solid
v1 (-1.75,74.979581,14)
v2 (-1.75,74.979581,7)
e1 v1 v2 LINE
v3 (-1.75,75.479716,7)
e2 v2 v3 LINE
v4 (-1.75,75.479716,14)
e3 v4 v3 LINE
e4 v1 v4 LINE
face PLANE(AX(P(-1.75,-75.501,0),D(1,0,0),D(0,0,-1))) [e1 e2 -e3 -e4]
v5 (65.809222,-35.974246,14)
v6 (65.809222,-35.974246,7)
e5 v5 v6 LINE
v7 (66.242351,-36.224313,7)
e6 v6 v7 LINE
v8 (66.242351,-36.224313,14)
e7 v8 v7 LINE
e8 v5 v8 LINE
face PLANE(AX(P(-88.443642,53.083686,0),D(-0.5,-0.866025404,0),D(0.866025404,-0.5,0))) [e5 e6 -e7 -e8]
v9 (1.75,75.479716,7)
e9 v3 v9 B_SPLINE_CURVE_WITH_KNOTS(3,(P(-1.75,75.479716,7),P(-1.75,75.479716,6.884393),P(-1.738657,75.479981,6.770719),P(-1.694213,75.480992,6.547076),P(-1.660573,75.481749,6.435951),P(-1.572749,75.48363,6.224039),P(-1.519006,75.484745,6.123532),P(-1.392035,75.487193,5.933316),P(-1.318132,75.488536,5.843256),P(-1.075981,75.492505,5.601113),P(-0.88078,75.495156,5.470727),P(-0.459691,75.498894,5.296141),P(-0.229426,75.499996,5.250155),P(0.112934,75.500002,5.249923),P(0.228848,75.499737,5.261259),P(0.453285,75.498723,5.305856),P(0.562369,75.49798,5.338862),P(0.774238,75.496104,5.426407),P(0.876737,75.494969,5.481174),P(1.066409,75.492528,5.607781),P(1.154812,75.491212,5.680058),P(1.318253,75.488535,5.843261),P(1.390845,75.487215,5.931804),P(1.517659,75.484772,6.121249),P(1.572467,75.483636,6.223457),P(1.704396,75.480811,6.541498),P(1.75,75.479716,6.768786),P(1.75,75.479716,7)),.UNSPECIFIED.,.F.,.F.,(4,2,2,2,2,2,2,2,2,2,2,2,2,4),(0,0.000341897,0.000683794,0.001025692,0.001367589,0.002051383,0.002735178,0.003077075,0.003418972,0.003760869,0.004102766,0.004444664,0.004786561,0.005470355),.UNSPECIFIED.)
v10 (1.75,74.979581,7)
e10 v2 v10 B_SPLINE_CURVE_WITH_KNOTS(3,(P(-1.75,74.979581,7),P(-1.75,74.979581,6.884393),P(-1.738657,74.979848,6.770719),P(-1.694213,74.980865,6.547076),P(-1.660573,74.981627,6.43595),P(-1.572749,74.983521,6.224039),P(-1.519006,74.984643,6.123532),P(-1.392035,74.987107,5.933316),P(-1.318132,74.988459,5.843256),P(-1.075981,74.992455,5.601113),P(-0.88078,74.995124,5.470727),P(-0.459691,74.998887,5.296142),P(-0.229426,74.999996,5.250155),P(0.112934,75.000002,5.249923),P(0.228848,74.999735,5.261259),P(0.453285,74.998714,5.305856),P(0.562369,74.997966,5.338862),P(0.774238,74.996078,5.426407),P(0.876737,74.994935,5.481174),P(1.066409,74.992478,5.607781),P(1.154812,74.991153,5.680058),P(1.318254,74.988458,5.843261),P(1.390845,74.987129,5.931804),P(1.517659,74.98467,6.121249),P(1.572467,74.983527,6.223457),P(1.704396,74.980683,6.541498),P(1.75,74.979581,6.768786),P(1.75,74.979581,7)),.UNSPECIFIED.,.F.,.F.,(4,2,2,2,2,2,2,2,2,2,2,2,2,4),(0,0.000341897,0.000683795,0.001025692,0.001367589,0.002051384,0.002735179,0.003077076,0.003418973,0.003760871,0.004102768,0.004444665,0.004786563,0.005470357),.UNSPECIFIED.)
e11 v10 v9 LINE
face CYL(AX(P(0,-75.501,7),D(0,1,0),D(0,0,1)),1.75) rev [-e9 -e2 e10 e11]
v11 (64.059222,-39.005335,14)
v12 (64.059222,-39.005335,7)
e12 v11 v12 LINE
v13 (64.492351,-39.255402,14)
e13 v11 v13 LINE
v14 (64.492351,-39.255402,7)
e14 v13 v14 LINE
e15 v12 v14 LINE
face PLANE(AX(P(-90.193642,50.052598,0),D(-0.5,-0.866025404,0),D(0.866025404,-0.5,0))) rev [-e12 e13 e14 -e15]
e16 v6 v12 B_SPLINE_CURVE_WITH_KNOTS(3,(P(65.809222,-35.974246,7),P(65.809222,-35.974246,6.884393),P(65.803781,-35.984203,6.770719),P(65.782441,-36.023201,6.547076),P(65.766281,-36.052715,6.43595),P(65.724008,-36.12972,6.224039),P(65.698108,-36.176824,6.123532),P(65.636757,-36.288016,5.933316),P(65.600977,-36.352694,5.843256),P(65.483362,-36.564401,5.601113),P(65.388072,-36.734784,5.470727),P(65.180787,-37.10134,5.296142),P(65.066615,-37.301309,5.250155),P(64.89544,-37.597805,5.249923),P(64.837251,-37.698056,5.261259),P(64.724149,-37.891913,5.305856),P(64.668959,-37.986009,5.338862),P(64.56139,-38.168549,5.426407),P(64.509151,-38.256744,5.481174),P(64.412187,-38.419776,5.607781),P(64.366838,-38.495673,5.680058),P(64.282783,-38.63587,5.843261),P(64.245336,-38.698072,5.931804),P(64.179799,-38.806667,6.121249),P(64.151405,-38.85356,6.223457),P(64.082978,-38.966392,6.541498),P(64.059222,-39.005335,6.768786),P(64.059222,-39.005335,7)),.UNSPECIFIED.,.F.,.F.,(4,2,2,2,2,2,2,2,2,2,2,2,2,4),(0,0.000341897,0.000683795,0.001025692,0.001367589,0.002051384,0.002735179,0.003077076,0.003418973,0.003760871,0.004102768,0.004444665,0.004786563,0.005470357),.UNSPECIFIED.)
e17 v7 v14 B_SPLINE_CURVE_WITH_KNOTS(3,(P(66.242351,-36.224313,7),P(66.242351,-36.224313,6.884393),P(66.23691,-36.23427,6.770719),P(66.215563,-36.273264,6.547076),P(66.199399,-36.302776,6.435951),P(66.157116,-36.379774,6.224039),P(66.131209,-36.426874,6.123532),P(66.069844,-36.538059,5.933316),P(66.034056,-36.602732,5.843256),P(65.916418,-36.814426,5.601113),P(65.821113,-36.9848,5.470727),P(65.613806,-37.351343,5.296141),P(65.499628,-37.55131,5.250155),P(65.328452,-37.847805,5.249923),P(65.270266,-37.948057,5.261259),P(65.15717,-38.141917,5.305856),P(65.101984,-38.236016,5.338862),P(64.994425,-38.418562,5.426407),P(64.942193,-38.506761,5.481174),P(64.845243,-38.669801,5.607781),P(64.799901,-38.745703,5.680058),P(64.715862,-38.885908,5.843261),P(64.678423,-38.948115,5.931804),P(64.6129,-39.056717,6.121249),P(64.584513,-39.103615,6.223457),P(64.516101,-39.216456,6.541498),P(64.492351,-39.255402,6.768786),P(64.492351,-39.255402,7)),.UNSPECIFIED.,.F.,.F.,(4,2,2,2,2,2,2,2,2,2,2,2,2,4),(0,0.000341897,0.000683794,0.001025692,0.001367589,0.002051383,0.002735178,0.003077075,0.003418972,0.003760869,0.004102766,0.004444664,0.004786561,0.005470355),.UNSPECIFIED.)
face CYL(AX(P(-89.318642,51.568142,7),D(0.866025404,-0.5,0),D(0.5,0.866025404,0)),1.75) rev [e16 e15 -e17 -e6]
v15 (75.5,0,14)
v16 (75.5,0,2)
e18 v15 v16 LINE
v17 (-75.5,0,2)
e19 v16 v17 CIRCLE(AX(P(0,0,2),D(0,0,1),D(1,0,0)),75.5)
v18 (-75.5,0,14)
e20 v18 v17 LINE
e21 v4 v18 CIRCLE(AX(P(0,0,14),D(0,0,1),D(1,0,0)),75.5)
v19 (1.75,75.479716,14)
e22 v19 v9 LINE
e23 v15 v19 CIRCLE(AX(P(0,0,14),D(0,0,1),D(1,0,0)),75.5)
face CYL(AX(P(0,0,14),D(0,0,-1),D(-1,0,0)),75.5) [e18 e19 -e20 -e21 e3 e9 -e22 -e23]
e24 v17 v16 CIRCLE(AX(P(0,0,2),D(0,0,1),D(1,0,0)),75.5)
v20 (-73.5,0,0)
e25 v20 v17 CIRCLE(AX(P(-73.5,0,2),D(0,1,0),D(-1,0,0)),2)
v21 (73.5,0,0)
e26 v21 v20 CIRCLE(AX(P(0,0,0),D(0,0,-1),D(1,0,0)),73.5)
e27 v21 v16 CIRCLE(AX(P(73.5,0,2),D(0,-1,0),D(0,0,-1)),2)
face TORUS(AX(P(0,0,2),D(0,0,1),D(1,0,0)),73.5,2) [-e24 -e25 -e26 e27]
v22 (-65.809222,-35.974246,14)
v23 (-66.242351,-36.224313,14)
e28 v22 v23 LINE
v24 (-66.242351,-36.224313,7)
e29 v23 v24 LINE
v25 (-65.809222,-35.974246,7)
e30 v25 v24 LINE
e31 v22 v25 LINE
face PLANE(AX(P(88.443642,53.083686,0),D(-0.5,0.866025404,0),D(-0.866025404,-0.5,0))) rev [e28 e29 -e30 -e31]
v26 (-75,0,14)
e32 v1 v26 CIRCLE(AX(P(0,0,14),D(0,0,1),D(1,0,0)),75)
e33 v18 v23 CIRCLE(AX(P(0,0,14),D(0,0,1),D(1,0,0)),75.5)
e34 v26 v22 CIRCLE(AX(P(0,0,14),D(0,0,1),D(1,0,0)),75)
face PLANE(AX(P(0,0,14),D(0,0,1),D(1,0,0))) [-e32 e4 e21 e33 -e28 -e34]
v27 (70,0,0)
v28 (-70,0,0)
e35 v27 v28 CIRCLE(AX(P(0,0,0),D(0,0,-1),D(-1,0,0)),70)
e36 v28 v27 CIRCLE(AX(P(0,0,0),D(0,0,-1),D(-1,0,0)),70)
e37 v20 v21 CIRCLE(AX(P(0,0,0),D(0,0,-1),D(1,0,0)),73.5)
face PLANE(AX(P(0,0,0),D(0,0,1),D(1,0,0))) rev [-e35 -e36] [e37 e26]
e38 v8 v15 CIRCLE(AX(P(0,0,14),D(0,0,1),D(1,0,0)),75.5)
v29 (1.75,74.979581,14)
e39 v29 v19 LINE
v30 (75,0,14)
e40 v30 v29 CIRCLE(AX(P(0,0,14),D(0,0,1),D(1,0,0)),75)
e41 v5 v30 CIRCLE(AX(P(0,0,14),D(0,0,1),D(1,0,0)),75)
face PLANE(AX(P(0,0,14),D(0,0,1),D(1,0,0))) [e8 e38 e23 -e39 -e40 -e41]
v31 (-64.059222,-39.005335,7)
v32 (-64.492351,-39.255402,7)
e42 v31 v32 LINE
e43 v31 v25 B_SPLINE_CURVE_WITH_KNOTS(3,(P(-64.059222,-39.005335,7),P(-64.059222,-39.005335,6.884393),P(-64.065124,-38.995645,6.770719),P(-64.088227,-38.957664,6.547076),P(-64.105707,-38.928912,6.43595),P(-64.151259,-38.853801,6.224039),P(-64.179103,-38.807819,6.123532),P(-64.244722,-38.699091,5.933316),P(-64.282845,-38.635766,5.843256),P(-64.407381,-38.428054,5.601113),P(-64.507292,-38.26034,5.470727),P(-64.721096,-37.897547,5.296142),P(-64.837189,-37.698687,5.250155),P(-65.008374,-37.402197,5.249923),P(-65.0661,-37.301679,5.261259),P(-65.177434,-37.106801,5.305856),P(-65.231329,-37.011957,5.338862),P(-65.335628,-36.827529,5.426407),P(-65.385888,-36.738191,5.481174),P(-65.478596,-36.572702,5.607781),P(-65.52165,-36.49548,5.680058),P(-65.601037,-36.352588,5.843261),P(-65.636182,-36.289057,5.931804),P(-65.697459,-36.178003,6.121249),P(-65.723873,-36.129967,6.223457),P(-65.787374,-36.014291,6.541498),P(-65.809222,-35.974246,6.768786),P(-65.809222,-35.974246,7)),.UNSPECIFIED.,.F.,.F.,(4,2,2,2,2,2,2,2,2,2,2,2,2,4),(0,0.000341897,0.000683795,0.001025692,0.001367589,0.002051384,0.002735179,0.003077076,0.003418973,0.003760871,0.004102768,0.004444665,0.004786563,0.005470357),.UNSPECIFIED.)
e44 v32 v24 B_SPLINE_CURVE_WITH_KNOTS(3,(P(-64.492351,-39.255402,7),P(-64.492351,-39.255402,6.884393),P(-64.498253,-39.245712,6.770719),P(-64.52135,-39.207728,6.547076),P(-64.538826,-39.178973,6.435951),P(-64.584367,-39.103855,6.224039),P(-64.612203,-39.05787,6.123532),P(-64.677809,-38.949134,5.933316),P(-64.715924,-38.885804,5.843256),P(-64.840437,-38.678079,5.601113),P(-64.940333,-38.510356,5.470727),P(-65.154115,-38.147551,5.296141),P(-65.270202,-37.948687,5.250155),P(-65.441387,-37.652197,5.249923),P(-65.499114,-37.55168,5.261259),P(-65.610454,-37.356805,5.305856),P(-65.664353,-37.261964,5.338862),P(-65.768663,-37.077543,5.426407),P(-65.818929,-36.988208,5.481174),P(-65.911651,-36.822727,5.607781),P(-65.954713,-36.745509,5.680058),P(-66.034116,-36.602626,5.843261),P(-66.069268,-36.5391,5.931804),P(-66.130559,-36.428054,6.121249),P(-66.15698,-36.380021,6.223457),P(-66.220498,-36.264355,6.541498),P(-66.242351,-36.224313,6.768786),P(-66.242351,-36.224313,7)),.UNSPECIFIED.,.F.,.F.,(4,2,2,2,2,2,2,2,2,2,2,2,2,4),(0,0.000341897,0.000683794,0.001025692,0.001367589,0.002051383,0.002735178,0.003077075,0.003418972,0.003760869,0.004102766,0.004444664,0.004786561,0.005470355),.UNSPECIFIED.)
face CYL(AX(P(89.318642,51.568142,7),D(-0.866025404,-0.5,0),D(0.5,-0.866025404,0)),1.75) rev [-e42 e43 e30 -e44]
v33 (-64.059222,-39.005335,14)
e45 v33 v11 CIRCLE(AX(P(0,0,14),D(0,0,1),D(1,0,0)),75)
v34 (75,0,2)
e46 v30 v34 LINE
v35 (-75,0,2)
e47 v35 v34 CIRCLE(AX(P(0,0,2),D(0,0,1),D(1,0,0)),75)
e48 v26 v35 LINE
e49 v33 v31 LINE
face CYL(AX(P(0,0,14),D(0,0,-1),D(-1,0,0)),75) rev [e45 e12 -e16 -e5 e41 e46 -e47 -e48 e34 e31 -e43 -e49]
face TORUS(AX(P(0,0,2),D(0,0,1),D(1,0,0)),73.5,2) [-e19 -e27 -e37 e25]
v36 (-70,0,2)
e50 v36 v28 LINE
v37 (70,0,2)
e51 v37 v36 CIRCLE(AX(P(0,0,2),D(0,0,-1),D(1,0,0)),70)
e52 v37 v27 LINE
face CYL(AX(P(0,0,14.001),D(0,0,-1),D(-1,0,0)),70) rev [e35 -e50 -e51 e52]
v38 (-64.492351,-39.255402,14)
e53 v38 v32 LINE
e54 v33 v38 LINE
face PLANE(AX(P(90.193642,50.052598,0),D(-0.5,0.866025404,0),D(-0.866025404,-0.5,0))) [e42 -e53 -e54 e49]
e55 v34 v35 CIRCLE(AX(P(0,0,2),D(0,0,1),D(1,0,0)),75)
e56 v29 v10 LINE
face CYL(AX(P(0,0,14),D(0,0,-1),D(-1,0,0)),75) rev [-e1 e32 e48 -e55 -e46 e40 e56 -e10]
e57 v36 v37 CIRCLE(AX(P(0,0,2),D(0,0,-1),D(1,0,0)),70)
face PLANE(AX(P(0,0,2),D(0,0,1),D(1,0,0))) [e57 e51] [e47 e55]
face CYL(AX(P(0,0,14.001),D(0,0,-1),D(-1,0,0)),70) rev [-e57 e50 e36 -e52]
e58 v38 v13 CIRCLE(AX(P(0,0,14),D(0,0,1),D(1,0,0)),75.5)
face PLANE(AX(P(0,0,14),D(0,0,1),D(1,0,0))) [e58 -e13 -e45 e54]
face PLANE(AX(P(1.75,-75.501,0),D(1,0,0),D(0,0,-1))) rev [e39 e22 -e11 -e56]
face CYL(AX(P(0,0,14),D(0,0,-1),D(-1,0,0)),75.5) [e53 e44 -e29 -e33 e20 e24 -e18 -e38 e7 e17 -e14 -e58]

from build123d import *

# Parameters (mm, degrees)
SKETCH_1_R               = 75.5
SKETCH_1_R_2             = 75
BOSS_EXTRUDE_1_DEPTH     = 14
SKETCH_2_R               = 75
BOSS_EXTRUDE_2_DEPTH     = 2
CUT_EXTRUDE_1_REACH      = 109.687
SKETCH_3_R               = 70
CUT_EXTRUDE_3_REACH      = 171.403
CUT_EXTRUDE_3_END_RADIUS = 75
CIRCULAR_PATTERN_1_COUNT = 3
FILLET_1_R               = 2


with BuildPart() as part:
    # Sketch 1 → Boss-Extrude 1 (new body)
    with BuildSketch(Plane.XY):
        Circle(SKETCH_1_R)
        Circle(SKETCH_1_R_2, mode=Mode.SUBTRACT)
    extrude(amount=BOSS_EXTRUDE_1_DEPTH)

    # Sketch 2 → Boss-Extrude 2 (add)
    with BuildSketch(Plane.XY):
        Circle(SKETCH_2_R)
    extrude(amount=BOSS_EXTRUDE_2_DEPTH)

    # Sketch 3 → Cut-Extrude 1 (cut, up to next)
    with BuildSketch(Plane(origin=(0, 0, 0), x_dir=(-1, 0, 0), z_dir=(0, 0, -1)), mode=Mode.PRIVATE) as cut_extrude_1_sk1:
        Circle(SKETCH_3_R)
    cut_extrude_1_tool1 = extrude(cut_extrude_1_sk1.sketch, amount=-CUT_EXTRUDE_1_REACH, mode=Mode.PRIVATE) & part.part
    add(cut_extrude_1_tool1.solids().sort_by_distance((0, 0, 0))[0], mode=Mode.SUBTRACT)

    # Cut-Extrude 3: up to this cylinder (the profile starts outside it)
    cut_extrude_3_end = Plane(origin=(0, 0, 9.803668), z_dir=(0, 0, -1)) * Cylinder(CUT_EXTRUDE_3_END_RADIUS, 493.806, mode=Mode.PRIVATE)
    # Sketch 7 → Cut-Extrude 3 (cut, up to the surface)
    with BuildSketch(Plane(origin=(0, 75.5, 0), x_dir=(1, 0, 0), z_dir=(0, 1, 0)), mode=Mode.PRIVATE) as cut_extrude_3_sk1:
        with BuildLine():
            Line((0, -14), (0, -5.25))
            ThreePointArc((0, -5.25), (-1.237436867, -5.762563133), (-1.75, -7))
            Line((-1.75, -7), (-1.75, -14))
            Line((-1.75, -14), (0, -14))
        make_face()
    cut_extrude_3_tool1 = extrude(cut_extrude_3_sk1.sketch, amount=-CUT_EXTRUDE_3_REACH, mode=Mode.PRIVATE) - cut_extrude_3_end
    # Sketch 7 → Cut-Extrude 3 (cut, up to the surface)
    with BuildSketch(Plane(origin=(0, 75.5, 0), x_dir=(1, 0, 0), z_dir=(0, 1, 0)), mode=Mode.PRIVATE) as cut_extrude_3_sk2:
        with BuildLine():
            ThreePointArc((1.75, -7), (1.237436867, -5.762563133), (0, -5.25))
            Line((0, -5.25), (0, -14))
            Line((0, -14), (1.75, -14))
            Line((1.75, -14), (1.75, -7))
        make_face()
    cut_extrude_3_tool2 = extrude(cut_extrude_3_sk2.sketch, amount=-CUT_EXTRUDE_3_REACH, mode=Mode.PRIVATE) - cut_extrude_3_end
    cut_extrude_3 = cut_extrude_3_tool1.solids().sort_by_distance((-0.85329, 75.5, 9.803668))[0] + cut_extrude_3_tool2.solids().sort_by_distance((0.85329, 75.5, 9.803668))[0]
    add(cut_extrude_3, mode=Mode.SUBTRACT)

    # Circular pattern 1: Cut-Extrude 3 ×3 about axis
    circular_pattern_1_axis = Axis((0, 0, 0), (0, 0, 1))
    for i in range(1, CIRCULAR_PATTERN_1_COUNT):
        add(cut_extrude_3.rotate(circular_pattern_1_axis, i * 360 / CIRCULAR_PATTERN_1_COUNT), mode=Mode.SUBTRACT)

    # Fillet 1
    fillet_1_edges = [part.edges().sort_by_distance(p)[0] for p in [
        (-75.5, 0, 0),
    ]]
    fillet(fillet_1_edges, radius=FILLET_1_R)


solid = part.part
